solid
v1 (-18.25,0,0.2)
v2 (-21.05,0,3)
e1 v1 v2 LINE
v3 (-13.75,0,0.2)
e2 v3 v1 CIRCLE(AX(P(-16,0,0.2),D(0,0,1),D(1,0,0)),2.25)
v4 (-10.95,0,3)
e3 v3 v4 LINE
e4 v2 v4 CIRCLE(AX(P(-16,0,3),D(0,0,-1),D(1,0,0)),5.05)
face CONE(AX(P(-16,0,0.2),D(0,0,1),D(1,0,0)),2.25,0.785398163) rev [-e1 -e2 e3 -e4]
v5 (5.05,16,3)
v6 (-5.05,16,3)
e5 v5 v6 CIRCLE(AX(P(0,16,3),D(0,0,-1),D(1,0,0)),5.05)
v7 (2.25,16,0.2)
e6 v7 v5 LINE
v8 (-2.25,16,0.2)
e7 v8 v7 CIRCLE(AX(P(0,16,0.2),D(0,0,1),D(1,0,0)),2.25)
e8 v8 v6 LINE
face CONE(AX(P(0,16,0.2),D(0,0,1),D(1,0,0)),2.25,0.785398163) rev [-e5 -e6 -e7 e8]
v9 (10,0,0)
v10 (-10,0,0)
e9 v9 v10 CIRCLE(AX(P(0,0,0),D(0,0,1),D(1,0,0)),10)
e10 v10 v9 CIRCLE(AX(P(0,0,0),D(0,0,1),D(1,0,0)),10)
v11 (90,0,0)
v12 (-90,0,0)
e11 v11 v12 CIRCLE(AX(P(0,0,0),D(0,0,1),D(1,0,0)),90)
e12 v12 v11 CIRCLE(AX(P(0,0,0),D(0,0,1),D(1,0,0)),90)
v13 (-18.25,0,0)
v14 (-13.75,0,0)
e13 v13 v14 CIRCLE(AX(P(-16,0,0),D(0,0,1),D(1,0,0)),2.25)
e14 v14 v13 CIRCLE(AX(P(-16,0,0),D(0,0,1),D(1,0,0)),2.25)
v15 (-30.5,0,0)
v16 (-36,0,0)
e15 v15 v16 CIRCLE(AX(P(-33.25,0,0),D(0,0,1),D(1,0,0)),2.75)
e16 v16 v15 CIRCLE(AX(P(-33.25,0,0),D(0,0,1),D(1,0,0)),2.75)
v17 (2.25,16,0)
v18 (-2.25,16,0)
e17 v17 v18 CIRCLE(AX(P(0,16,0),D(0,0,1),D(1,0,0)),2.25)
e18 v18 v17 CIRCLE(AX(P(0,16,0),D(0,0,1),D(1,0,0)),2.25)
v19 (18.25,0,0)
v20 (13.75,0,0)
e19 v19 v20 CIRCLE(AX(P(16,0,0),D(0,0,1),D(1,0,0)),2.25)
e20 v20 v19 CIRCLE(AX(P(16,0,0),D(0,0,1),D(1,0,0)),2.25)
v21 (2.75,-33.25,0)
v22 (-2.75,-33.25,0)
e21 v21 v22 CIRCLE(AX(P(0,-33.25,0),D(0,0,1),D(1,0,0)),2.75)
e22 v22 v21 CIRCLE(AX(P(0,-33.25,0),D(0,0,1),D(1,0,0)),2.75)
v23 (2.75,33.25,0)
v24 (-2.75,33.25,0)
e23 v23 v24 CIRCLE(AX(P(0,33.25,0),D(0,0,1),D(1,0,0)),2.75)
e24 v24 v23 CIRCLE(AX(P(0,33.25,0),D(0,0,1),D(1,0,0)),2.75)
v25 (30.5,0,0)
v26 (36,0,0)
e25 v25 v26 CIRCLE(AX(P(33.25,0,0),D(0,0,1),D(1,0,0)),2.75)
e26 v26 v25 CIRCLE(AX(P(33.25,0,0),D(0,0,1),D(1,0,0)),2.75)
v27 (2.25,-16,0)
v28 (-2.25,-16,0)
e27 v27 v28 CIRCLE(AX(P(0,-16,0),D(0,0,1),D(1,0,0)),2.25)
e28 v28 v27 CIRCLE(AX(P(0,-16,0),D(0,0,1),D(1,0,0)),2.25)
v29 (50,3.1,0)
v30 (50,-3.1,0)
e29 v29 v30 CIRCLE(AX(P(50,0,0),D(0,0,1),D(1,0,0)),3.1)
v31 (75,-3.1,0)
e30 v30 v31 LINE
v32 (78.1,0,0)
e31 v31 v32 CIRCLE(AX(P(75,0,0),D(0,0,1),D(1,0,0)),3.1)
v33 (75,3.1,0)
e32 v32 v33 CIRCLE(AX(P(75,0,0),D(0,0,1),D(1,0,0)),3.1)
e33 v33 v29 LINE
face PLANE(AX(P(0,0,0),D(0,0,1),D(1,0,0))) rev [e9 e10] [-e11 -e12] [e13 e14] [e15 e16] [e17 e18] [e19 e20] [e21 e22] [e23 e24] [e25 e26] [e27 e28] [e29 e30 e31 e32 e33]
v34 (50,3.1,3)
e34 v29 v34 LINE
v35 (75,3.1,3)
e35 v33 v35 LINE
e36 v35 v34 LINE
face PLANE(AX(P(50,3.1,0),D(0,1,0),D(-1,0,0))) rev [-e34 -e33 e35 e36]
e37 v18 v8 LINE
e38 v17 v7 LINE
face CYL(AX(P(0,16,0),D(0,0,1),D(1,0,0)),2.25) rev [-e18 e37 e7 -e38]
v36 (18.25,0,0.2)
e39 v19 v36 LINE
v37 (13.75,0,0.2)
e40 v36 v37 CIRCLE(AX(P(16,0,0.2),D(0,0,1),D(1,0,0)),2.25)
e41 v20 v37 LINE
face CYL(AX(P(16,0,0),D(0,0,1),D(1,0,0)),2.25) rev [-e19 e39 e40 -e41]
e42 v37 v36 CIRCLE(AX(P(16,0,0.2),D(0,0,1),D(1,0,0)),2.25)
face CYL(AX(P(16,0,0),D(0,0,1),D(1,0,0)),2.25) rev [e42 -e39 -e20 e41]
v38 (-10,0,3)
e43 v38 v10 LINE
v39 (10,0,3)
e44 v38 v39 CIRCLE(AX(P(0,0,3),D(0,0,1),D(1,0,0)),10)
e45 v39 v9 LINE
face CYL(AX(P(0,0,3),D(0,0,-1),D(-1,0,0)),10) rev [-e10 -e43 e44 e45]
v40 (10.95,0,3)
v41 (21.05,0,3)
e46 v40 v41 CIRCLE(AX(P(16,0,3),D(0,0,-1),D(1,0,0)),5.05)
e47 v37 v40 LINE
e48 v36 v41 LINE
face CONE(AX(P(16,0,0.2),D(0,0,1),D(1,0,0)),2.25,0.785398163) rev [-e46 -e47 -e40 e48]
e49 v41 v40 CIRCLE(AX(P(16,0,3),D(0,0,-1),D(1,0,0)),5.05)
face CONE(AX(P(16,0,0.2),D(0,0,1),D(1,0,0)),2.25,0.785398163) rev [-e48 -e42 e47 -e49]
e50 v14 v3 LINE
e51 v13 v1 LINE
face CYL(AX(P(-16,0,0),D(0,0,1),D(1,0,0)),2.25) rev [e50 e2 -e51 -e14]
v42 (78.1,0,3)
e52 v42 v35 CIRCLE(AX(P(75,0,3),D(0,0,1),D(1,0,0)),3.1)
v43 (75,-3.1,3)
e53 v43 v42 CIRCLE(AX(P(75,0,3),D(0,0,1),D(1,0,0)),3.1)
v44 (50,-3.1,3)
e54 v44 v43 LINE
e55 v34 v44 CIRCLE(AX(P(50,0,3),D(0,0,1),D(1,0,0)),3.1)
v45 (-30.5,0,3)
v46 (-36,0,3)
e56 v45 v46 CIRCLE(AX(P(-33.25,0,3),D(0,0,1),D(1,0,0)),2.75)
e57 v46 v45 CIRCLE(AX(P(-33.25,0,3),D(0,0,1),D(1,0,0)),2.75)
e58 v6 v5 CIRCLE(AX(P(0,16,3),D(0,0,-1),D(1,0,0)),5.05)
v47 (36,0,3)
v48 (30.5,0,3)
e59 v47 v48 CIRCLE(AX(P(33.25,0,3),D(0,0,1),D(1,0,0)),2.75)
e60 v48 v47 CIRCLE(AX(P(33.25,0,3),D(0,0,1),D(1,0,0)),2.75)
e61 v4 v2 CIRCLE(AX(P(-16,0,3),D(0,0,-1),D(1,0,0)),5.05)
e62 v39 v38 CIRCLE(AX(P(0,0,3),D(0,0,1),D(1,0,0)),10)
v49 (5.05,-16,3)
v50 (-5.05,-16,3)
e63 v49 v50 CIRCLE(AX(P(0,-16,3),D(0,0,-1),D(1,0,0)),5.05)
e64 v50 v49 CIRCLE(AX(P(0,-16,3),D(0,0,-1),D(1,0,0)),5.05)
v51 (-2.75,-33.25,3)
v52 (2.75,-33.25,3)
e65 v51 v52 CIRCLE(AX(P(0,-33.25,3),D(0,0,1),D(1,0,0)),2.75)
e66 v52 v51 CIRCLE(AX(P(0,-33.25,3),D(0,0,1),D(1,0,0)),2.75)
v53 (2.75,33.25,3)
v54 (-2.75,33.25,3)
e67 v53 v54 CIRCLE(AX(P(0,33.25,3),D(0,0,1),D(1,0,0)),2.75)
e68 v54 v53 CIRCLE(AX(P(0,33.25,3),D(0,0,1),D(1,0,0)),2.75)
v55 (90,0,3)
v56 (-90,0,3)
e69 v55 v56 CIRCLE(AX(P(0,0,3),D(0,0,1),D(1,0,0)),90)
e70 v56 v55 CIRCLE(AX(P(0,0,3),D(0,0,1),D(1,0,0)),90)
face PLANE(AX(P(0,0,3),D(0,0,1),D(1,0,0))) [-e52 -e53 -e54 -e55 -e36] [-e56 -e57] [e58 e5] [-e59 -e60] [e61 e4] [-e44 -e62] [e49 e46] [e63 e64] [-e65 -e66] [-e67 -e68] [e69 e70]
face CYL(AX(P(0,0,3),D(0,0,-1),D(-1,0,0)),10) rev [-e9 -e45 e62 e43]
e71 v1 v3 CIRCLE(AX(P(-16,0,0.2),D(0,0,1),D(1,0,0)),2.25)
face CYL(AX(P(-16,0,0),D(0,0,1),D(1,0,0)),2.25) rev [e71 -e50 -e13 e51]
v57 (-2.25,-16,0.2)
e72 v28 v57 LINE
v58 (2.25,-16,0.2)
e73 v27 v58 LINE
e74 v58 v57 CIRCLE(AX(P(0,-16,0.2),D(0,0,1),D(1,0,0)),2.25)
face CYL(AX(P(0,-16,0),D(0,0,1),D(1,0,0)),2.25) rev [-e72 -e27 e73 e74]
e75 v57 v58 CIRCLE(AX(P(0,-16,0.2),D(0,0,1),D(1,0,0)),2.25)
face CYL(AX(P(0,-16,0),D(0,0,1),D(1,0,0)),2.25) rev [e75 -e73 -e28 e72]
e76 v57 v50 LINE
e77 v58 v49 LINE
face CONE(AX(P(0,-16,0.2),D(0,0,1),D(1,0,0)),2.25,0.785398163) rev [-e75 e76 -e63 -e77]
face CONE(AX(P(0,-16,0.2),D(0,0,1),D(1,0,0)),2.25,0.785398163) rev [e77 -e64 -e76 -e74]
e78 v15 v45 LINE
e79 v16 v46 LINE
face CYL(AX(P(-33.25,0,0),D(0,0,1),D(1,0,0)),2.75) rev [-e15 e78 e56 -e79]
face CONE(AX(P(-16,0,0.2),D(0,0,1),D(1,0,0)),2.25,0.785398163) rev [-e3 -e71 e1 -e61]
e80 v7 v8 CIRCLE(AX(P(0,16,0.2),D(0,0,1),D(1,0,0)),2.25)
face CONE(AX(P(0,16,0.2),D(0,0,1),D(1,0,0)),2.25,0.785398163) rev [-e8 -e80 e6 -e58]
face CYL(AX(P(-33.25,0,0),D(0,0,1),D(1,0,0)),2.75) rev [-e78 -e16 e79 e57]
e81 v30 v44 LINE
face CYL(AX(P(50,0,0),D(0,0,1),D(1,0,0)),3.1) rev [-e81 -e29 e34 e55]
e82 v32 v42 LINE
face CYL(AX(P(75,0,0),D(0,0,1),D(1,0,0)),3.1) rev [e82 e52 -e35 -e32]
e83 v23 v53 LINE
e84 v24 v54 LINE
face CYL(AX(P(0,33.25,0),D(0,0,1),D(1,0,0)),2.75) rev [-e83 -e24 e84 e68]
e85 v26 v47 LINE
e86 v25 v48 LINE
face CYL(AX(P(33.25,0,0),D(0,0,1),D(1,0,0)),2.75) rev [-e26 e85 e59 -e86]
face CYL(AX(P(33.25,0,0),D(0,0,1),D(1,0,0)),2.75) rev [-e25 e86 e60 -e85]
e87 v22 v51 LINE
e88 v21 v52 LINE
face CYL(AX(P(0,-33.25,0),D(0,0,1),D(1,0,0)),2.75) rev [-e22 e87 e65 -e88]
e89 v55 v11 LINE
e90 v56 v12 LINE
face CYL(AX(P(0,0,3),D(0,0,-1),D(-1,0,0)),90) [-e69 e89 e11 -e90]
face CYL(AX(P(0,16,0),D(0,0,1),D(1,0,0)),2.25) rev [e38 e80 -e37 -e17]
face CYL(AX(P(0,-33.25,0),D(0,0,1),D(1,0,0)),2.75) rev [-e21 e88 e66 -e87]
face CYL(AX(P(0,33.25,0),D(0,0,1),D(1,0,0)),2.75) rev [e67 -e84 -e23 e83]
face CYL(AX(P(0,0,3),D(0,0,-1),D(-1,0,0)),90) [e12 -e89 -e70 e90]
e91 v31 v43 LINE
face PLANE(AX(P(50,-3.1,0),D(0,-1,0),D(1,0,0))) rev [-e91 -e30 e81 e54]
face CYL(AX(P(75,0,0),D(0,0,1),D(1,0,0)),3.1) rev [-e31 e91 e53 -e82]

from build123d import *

# Parameters (mm, degrees)
SKETCH1_R           = 90
SKETCH1_R_2         = 10
BOSS_EXTRUDE1_DEPTH = 3
SKETCH2_R           = 2.25
SKETCH2_R_2         = 2.75
CUT_EXTRUDE1_DEPTH  = 3
CHAMFER1_SIZE       = 2.8


with BuildPart() as part:
    # Sketch1 → Boss-Extrude1 (new body)
    with BuildSketch(Plane.XY):
        Circle(SKETCH1_R)
        Circle(SKETCH1_R_2, mode=Mode.SUBTRACT)
    extrude(amount=BOSS_EXTRUDE1_DEPTH)

    # Sketch2 → Cut-Extrude1 (cut)
    with BuildSketch(Plane.XY.offset(3)):
        with Locations((0, 16)):
            Circle(SKETCH2_R)
        with Locations((-16, 0)):
            Circle(SKETCH2_R)
        with Locations((0, -16)):
            Circle(SKETCH2_R)
        with Locations((16, 0)):
            Circle(SKETCH2_R)
        with Locations((0, 33.25)):
            Circle(SKETCH2_R_2)
        with Locations((-33.25, 0)):
            Circle(SKETCH2_R_2)
        with Locations((0, -33.25)):
            Circle(SKETCH2_R_2)
        with Locations((33.25, 0)):
            Circle(SKETCH2_R_2)
        with BuildLine():
            Line((50, 3.1), (75, 3.1))
            ThreePointArc((75, 3.1), (78.1, 0), (75, -3.1))
            Line((75, -3.1), (50, -3.1))
            ThreePointArc((50, -3.1), (46.9, 0), (50, 3.1))
        make_face()
    extrude(amount=-CUT_EXTRUDE1_DEPTH, mode=Mode.SUBTRACT)

    # Chamfer1
    chamfer1_edges = [part.edges().sort_by_distance(p)[0] for p in [
        (-2.25, 16, 3),
        (-18.25, 0, 3),
        (-2.25, -16, 3),
        (13.75, 0, 3),
    ]]
    chamfer(chamfer1_edges, length=CHAMFER1_SIZE)


solid = part.part
